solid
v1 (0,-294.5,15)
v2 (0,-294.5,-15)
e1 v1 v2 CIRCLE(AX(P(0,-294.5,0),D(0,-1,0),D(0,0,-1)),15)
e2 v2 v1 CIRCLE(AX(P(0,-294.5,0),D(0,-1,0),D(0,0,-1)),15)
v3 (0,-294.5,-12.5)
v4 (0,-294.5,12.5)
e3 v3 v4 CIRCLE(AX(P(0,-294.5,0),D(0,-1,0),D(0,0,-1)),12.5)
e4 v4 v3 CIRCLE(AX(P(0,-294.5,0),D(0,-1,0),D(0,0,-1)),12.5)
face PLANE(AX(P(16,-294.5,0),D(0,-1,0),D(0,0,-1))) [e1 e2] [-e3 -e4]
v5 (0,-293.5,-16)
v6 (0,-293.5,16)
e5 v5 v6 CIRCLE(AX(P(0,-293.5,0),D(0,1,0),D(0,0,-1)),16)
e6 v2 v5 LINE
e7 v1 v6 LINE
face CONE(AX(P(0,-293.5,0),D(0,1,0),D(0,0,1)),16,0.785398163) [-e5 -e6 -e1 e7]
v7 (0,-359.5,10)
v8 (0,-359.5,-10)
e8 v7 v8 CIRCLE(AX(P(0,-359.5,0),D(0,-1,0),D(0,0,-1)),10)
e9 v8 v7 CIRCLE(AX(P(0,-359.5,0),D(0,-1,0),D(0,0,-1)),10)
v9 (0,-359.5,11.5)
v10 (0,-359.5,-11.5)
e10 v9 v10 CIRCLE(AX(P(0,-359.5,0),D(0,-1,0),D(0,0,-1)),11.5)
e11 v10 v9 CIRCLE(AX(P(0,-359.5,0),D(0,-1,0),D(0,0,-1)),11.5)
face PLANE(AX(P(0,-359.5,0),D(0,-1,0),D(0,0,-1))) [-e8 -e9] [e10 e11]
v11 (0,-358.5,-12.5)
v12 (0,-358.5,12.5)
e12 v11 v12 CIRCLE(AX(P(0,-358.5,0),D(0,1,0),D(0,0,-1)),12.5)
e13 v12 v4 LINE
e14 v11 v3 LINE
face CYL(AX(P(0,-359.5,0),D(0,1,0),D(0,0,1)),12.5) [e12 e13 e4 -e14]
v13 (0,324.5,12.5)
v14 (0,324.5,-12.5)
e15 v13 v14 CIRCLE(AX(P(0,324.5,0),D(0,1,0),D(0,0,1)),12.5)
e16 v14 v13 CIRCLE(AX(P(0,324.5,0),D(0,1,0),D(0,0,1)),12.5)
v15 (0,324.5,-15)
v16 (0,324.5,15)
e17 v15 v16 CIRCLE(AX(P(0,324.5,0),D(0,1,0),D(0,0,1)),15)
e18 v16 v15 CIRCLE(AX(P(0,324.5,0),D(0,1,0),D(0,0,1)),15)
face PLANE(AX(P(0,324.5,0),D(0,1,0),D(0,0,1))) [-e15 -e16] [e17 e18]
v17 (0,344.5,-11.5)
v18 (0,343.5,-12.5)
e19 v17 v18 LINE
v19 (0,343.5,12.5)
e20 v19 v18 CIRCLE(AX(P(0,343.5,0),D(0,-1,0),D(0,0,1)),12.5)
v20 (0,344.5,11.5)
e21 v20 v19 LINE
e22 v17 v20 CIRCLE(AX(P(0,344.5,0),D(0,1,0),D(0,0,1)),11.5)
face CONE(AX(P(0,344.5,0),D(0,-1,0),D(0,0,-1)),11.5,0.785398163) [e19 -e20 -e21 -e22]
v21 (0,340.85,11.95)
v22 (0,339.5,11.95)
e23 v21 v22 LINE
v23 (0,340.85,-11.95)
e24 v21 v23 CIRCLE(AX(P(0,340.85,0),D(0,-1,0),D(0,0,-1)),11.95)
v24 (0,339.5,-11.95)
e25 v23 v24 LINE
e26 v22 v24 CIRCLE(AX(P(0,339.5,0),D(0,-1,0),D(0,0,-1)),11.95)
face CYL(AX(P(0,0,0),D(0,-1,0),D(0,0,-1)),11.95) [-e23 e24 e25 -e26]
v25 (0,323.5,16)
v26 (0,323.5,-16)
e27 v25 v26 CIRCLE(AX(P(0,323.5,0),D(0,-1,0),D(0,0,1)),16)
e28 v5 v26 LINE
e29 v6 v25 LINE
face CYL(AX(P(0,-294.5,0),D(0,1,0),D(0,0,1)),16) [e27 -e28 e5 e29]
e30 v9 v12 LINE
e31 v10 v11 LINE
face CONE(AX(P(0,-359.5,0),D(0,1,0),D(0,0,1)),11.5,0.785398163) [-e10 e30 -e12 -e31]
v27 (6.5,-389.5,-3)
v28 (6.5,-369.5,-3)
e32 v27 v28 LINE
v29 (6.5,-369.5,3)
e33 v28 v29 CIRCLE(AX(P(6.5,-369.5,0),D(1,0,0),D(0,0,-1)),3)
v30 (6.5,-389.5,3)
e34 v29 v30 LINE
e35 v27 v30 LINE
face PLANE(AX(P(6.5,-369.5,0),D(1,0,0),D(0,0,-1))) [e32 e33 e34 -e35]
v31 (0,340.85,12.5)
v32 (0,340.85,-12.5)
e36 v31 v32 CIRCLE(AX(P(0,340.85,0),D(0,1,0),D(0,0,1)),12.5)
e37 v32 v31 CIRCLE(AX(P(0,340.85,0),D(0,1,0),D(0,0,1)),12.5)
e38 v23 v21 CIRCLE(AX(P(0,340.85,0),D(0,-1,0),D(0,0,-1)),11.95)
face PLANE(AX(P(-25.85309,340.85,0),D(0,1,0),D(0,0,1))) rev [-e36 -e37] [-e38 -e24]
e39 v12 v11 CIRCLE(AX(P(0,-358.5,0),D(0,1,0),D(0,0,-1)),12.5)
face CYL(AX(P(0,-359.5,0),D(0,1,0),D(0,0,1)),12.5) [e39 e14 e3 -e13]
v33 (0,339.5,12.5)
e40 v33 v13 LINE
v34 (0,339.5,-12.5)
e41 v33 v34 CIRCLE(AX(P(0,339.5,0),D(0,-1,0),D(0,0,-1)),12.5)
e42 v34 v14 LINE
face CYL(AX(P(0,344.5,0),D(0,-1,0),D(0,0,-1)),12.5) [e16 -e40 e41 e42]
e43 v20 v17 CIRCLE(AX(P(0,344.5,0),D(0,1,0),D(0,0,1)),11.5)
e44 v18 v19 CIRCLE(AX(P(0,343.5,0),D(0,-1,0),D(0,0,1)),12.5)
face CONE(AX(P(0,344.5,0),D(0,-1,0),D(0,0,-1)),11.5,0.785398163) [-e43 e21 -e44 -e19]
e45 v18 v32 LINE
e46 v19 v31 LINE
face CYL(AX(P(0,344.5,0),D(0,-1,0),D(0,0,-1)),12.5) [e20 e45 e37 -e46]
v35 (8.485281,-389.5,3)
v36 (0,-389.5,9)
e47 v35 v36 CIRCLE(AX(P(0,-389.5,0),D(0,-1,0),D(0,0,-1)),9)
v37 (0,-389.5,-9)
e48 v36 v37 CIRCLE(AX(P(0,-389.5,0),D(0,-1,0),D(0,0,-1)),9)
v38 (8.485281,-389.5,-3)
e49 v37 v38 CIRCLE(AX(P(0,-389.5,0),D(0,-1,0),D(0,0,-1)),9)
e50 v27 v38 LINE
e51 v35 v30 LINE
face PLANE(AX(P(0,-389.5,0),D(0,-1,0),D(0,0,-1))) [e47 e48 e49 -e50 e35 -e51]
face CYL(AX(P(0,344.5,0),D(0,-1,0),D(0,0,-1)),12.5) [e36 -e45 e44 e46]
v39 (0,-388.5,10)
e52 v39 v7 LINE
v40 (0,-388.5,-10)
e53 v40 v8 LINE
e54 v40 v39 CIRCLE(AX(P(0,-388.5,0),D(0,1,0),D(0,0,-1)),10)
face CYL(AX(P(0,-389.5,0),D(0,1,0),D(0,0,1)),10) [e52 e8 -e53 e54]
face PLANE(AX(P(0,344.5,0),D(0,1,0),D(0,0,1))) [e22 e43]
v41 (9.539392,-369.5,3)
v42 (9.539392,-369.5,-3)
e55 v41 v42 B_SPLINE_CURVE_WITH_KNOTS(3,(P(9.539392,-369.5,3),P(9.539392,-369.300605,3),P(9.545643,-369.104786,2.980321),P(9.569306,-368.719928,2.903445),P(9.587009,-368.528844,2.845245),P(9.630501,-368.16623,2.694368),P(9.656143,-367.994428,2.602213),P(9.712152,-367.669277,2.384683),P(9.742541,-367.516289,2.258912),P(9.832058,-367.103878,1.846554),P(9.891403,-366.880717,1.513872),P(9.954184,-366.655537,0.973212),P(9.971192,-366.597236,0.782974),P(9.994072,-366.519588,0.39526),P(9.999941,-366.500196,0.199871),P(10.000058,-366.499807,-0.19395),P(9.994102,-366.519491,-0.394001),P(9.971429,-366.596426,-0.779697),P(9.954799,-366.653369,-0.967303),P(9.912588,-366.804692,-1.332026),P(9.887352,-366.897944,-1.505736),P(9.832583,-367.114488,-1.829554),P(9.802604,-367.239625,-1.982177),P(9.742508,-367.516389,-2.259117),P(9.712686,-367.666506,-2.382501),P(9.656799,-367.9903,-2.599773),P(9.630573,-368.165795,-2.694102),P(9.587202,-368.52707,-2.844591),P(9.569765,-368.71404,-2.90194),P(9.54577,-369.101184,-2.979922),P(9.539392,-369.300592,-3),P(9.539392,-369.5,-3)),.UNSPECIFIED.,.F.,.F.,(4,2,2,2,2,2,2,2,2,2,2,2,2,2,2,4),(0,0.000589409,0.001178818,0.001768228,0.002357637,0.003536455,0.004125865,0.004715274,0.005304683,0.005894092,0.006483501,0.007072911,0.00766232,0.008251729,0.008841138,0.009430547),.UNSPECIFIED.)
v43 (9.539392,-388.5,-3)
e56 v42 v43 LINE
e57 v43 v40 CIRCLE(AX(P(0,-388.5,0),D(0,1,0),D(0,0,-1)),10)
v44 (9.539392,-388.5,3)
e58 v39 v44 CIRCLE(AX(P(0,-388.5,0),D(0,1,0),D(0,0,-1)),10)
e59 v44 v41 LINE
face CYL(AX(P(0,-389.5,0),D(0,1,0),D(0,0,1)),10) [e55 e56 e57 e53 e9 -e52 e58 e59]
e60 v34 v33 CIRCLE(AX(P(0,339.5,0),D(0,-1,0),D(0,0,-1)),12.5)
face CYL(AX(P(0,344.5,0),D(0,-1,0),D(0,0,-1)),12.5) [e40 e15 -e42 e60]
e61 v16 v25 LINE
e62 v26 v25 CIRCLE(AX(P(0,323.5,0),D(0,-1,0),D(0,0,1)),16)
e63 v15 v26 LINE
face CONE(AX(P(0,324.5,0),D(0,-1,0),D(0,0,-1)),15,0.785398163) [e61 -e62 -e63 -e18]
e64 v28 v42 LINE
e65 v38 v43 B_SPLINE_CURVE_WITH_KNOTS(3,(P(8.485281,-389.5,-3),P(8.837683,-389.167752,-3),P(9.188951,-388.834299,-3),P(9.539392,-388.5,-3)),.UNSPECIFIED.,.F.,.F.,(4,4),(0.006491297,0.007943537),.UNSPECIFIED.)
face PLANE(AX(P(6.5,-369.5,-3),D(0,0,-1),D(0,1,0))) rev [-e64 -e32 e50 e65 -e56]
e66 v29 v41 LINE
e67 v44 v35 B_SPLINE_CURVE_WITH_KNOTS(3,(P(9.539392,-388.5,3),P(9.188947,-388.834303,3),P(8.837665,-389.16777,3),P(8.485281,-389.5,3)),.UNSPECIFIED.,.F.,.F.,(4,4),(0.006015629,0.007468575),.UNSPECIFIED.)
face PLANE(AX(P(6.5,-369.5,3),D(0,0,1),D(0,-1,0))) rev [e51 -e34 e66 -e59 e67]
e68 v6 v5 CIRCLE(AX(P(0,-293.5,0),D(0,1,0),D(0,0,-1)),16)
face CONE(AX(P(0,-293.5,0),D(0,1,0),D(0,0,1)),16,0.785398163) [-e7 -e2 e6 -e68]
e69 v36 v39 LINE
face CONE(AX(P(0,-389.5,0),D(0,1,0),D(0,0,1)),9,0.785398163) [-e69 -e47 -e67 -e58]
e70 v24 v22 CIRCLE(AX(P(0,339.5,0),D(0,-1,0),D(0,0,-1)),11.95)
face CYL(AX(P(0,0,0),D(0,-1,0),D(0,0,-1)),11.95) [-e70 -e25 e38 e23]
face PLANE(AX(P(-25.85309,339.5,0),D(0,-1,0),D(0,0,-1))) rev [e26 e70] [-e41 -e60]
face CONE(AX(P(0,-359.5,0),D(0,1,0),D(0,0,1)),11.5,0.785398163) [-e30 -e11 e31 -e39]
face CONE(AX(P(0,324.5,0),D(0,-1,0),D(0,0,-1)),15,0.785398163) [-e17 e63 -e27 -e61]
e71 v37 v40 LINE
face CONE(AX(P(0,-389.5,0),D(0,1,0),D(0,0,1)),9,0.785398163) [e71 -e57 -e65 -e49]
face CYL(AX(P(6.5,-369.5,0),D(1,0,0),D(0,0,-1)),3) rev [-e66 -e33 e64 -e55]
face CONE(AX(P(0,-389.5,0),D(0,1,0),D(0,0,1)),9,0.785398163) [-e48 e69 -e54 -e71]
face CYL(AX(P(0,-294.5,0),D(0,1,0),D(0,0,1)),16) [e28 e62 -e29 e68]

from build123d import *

# Parameters (mm, degrees)
SKETCH_5_W          = 16
SKETCH_5_H          = 619
SKETCH_6_R          = 12.5
EXTRUDE_1_DEPTH     = 65
SKETCH_7_R          = 10
EXTRUDE_2_DEPTH     = 30
EXTRUDE_START       = 20
SKETCH_8_R          = 12.5
EXTRUDE_3_DEPTH     = 20
SKETCH_9_W          = 13.903089526
SKETCH_9_H          = 1.35
CHAMFER_1_SIZE      = 1
CUT_EXTRUDE_1_DEPTH = 3.5


with BuildPart() as part:
    # 草图5 → 旋转2 (revolve)
    with BuildSketch(Plane(origin=(0, 0, 0), x_dir=(-1, 0, 0), z_dir=(0, 0, -1)), mode=Mode.PRIVATE) as revolve_2_sk:
        with Locations((-8, 15)):
            Rectangle(SKETCH_5_W, SKETCH_5_H)
    revolve(revolve_2_sk.sketch.rotate(Axis((0, -294.5, 0), (0, 1, 0)), 270), axis=Axis((0, -294.5, 0), (0, 1, 0)))

    # 草图6 → 凸台-拉伸1 (add)
    with BuildSketch(Plane.XZ.offset(294.5)):
        with Locations(Location((0, 0, 0), (0, 0, 270))):
            Circle(SKETCH_6_R)
    extrude(amount=EXTRUDE_1_DEPTH)

    # 草图7 → 凸台-拉伸2 (add)
    with BuildSketch(Plane.XZ.offset(359.5)):
        with Locations(Location((0, 0, 0), (0, 0, 270))):
            Circle(SKETCH_7_R)
    extrude(amount=EXTRUDE_2_DEPTH)

    # 草图8 → 凸台-拉伸3 (add)
    with BuildSketch(Plane(origin=(0, 324.5, 0), x_dir=(1, 0, 0), z_dir=(0, 1, 0)).offset(EXTRUDE_START)):
        with Locations(Location((0, 0, 0), (0, 0, 90))):
            Circle(SKETCH_8_R)
    extrude(amount=-EXTRUDE_3_DEPTH)

    # 草图9 → 切除-旋转1 (revolve, cut)
    with BuildSketch(Plane(origin=(0, 0, 0), x_dir=(-1, 0, 0), z_dir=(0, 0, -1)), mode=Mode.PRIVATE) as cut_revolve_1_sk:
        with Locations((18.901544763, 340.175)):
            Rectangle(SKETCH_9_W, SKETCH_9_H)
    revolve(cut_revolve_1_sk.sketch.rotate(Axis((0, 0, 0), (0, 1, 0)), 270), axis=Axis((0, 0, 0), (0, 1, 0)), mode=Mode.SUBTRACT)

    # 倒角1
    chamfer_1_edges = [part.edges().sort_by_distance(p)[0] for p in [
        (0, -359.5, 12.5),
        (0, -389.5, 10),
        (0, 344.5, 12.5),
        (0, 324.5, -16),
        (0, -294.5, -16),
    ]]
    chamfer(chamfer_1_edges, length=CHAMFER_1_SIZE)

    # 草图10 → 切除-拉伸1 (cut)
    with BuildSketch(Plane(origin=(10, 0, 0), x_dir=(0, 0, -1), z_dir=(1, 0, 0))):
        with BuildLine():
            Line((3, -369.5), (3, -402.553548126))
            ThreePointArc((3, -402.553548126), (0, -405.553548126), (-3, -402.553548126))
            Line((-3, -402.553548126), (-3, -369.5))
            ThreePointArc((-3, -369.5), (0, -366.5), (3, -369.5))
        make_face()
    extrude(amount=-CUT_EXTRUDE_1_DEPTH, mode=Mode.SUBTRACT)


solid = part.part
